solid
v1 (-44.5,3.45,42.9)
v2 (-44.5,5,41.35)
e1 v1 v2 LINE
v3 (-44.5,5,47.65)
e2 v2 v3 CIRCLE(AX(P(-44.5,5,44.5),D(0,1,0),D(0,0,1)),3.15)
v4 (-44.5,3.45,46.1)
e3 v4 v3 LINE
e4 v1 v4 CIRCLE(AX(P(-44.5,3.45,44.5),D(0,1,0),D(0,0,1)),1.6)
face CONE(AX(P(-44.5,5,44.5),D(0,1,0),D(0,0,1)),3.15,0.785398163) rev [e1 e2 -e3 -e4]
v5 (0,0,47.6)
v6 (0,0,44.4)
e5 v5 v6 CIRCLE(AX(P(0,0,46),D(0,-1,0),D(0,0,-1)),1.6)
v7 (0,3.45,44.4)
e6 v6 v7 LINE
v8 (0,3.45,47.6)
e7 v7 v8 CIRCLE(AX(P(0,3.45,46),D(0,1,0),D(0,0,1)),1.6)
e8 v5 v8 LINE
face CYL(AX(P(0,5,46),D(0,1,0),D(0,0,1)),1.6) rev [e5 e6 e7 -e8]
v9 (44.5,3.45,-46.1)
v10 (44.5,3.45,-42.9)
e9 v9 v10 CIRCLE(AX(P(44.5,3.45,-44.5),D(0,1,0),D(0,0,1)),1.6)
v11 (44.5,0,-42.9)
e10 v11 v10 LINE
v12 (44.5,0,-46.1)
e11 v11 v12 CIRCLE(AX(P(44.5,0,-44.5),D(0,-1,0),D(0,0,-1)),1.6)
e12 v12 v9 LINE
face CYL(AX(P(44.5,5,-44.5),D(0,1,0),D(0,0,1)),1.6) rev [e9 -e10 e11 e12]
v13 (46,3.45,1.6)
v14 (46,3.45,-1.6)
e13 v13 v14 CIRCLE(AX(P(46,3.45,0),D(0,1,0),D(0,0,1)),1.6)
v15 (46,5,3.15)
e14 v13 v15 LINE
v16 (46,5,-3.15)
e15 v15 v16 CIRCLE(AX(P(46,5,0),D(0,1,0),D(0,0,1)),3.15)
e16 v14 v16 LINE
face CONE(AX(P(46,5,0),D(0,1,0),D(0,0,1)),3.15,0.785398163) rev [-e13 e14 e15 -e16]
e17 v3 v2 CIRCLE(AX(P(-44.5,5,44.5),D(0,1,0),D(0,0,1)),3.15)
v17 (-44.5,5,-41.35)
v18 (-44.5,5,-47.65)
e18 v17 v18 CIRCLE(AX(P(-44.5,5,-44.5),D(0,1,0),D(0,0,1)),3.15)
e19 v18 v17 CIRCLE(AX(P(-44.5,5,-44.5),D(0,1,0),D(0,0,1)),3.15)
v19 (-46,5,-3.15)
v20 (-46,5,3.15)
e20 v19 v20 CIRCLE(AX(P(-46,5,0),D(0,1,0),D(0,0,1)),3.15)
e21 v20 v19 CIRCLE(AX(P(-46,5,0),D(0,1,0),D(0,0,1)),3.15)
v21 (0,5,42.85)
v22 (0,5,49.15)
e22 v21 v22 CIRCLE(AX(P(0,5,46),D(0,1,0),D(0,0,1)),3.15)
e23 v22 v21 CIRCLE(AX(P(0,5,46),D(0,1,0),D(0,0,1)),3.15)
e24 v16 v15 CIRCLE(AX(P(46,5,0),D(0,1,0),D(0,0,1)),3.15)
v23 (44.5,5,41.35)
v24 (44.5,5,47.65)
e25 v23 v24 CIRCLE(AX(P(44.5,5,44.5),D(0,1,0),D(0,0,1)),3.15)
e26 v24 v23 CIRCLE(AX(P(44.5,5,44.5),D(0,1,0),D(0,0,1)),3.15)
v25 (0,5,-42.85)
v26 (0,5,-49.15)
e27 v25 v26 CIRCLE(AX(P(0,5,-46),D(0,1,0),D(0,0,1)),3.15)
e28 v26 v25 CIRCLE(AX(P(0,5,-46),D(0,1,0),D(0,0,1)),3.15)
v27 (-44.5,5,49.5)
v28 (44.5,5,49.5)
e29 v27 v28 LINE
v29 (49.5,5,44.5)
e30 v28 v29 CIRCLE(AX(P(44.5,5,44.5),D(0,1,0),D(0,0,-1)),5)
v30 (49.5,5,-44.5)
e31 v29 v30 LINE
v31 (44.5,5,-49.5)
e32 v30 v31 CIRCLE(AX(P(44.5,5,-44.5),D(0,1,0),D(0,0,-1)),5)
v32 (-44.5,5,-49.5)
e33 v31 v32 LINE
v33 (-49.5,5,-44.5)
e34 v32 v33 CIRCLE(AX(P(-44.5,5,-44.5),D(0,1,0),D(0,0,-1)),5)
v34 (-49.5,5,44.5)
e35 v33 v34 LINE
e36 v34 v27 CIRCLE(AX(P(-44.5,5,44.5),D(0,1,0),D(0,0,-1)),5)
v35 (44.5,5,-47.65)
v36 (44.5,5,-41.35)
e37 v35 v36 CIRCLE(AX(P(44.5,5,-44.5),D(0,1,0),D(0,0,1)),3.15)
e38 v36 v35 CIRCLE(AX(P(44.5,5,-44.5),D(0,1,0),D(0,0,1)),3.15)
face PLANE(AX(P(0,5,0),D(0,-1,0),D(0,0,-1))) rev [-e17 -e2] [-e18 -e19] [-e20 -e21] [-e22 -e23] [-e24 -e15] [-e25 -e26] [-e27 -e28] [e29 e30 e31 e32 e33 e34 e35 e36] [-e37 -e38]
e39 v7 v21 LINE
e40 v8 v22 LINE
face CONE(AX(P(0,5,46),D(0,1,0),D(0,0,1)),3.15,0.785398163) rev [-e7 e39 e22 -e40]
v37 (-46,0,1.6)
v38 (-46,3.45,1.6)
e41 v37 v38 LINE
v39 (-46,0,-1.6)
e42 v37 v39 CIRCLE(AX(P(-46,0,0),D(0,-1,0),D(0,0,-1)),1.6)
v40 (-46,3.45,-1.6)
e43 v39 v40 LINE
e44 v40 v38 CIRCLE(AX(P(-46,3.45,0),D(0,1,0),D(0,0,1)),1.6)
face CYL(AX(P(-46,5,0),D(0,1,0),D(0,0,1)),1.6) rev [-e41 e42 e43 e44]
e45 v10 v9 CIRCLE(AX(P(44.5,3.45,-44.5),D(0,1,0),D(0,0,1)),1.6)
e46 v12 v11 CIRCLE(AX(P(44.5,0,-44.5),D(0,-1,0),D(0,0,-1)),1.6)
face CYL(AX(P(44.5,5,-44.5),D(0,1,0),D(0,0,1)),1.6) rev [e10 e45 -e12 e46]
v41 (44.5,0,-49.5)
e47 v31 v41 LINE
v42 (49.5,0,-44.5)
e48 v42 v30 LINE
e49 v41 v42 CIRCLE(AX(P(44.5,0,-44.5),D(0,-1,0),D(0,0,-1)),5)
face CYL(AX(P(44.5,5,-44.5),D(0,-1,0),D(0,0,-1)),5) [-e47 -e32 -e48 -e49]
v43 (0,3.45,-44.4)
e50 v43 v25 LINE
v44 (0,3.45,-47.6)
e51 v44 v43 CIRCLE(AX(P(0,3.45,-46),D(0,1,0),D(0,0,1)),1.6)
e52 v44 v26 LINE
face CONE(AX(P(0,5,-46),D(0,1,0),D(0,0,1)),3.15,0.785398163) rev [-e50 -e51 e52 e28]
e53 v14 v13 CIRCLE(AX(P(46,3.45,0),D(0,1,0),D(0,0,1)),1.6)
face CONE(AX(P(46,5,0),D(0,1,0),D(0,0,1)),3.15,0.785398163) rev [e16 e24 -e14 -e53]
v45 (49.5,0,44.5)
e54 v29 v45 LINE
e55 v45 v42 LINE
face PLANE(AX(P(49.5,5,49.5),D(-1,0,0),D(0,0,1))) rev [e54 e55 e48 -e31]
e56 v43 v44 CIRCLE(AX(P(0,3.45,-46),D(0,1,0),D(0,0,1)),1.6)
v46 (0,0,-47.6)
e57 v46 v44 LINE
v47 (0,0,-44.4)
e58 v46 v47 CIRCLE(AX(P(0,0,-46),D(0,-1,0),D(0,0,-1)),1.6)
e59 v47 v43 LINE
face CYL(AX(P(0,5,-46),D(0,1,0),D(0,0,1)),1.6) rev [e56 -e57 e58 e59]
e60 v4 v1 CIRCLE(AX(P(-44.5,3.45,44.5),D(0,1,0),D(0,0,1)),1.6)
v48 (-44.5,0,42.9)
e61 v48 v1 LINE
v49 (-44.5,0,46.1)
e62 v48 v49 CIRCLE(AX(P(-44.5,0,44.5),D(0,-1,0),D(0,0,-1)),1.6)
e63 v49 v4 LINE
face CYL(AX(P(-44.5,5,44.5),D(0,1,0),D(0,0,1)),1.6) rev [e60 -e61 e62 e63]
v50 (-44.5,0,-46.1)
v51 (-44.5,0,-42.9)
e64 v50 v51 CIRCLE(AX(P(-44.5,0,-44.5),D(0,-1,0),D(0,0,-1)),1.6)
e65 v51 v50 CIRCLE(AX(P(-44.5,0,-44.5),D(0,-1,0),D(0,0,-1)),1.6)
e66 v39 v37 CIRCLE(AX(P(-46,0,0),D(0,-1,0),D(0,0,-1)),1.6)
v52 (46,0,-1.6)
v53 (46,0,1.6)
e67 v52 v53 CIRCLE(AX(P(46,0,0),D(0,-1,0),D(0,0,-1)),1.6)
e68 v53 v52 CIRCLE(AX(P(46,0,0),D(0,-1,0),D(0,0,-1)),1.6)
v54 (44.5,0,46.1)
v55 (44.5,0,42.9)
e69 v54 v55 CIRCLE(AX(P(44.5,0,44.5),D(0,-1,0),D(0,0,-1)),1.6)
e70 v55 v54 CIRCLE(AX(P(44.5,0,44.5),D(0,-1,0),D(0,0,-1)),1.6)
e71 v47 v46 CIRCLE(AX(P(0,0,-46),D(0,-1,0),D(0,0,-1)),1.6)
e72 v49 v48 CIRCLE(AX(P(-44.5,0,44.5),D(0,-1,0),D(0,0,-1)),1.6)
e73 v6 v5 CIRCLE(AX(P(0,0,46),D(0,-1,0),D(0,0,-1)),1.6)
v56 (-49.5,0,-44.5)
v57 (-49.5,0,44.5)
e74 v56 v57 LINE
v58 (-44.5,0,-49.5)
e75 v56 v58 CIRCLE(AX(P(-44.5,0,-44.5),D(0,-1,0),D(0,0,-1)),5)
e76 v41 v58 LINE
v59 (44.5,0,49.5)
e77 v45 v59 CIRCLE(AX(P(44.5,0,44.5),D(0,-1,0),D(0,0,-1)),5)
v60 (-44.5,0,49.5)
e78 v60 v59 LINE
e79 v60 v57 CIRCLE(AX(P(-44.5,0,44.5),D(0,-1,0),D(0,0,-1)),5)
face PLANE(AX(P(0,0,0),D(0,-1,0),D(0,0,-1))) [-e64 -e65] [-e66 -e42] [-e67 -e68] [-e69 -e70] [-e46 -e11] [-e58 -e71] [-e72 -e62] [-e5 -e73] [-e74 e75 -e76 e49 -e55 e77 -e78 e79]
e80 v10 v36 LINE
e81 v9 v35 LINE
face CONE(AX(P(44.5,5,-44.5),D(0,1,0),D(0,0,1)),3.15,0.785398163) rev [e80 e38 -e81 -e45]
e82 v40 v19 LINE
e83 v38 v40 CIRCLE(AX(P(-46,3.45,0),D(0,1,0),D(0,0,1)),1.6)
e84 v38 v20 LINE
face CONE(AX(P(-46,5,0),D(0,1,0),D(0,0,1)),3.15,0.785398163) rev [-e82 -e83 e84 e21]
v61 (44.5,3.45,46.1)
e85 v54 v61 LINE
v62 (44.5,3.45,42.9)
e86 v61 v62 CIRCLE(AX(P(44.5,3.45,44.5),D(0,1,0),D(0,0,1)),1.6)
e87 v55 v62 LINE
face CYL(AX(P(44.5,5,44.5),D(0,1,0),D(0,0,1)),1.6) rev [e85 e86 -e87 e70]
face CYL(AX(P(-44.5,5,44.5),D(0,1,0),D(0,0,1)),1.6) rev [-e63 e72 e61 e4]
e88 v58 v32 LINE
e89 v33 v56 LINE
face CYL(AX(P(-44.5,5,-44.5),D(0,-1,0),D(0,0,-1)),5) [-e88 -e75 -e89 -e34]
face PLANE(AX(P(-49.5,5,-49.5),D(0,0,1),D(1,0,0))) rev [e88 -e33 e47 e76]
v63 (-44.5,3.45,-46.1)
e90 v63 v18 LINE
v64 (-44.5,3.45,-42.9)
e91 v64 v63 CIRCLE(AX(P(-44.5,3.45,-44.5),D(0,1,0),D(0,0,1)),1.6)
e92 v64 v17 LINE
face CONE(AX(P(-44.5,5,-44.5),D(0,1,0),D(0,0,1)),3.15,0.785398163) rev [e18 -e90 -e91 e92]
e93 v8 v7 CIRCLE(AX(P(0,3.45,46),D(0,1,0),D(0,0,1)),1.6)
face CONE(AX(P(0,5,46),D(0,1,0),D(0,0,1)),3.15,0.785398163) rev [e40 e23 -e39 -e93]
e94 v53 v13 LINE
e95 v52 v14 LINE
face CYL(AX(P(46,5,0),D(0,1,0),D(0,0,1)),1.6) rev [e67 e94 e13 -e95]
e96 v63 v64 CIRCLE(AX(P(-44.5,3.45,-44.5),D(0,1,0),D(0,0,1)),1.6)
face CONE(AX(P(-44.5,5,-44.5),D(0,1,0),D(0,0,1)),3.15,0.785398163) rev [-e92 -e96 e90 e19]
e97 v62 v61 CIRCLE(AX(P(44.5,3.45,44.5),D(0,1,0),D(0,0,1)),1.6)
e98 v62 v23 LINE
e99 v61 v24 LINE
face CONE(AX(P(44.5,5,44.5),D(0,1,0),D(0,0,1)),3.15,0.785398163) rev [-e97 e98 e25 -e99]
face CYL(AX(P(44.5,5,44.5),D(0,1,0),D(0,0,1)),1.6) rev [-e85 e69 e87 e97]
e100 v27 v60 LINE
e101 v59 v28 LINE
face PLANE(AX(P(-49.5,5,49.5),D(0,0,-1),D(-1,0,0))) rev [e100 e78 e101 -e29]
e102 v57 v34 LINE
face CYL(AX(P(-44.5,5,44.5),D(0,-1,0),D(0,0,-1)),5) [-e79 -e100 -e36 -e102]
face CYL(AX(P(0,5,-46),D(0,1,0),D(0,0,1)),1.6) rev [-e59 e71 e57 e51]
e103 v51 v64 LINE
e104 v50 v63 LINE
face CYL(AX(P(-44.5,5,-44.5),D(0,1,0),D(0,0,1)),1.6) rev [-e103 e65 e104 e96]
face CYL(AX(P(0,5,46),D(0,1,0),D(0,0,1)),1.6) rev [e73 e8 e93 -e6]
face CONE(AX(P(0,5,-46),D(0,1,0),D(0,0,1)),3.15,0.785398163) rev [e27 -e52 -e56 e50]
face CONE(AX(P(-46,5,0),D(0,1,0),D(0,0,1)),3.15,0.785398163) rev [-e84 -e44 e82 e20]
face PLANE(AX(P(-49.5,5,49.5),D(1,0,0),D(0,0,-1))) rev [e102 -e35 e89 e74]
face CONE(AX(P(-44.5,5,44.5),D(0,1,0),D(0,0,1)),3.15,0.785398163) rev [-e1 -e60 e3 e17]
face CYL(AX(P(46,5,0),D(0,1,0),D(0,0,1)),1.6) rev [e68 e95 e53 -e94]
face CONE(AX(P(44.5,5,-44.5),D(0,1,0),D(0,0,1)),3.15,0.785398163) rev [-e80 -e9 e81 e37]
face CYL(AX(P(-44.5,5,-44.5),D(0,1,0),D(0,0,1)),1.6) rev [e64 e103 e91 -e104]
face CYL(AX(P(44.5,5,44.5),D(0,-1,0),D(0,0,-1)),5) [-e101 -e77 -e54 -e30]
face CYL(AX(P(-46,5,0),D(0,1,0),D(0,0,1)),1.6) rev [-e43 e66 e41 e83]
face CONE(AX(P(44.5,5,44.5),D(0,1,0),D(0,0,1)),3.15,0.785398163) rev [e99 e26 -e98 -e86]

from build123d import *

# Parameters (mm, degrees)
SKETCH1_W                                       = 99
SKETCH1_H                                       = 99
BOSS_EXTRUDE1_DEPTH                             = 5
FILLET1_R                                       = 5
CSK_FOR_M3_FLAT_HEAD_MACHINE_SCREW1_D           = 3.2
CSK_FOR_M3_FLAT_HEAD_MACHINE_SCREW1_DEPTH       = 8.5
CSK_FOR_M3_FLAT_HEAD_MACHINE_SCREW1_CSINK_D     = 6.3
CSK_FOR_M3_FLAT_HEAD_MACHINE_SCREW1_CSINK_ANGLE = 90
CSK_FOR_M3_FLAT_HEAD_MACHINE_SCREW1_TIP         = 0.96137699


with BuildPart() as part:
    # Sketch1 → Boss-Extrude1 (new body)
    with BuildSketch(Plane(origin=(0, 0, 0), x_dir=(1, 0, 0), z_dir=(0, 1, 0))):
        Rectangle(SKETCH1_W, SKETCH1_H)
    extrude(amount=BOSS_EXTRUDE1_DEPTH)

    # Fillet1
    fillet1_edges = [part.edges().sort_by_distance(p)[0] for p in [
        (49.5, 2.5, 49.5),
        (-49.5, 2.5, 49.5),
        (-49.5, 2.5, -49.5),
        (49.5, 2.5, -49.5),
    ]]
    fillet(fillet1_edges, radius=FILLET1_R)

    # CSK for M3 Flat Head Machine Screw1
    with Locations(Plane(origin=(0, 5, 0), x_dir=(1, 0, 0), z_dir=(0, 1, 0))):
        with Locations((-44.5, 44.5), (44.5, 44.5), (0, 46), (-46, 0), (-44.5, -44.5), (0, -46), (44.5, -44.5), (46, 0)):
            CounterSinkHole(CSK_FOR_M3_FLAT_HEAD_MACHINE_SCREW1_D / 2, CSK_FOR_M3_FLAT_HEAD_MACHINE_SCREW1_CSINK_D / 2, depth=CSK_FOR_M3_FLAT_HEAD_MACHINE_SCREW1_DEPTH, counter_sink_angle=CSK_FOR_M3_FLAT_HEAD_MACHINE_SCREW1_CSINK_ANGLE)
            with Locations((0, 0, -(CSK_FOR_M3_FLAT_HEAD_MACHINE_SCREW1_DEPTH + CSK_FOR_M3_FLAT_HEAD_MACHINE_SCREW1_TIP / 2))):  # 118° drill point
                Cone(0, CSK_FOR_M3_FLAT_HEAD_MACHINE_SCREW1_D / 2, CSK_FOR_M3_FLAT_HEAD_MACHINE_SCREW1_TIP, mode=Mode.SUBTRACT)


solid = part.part
